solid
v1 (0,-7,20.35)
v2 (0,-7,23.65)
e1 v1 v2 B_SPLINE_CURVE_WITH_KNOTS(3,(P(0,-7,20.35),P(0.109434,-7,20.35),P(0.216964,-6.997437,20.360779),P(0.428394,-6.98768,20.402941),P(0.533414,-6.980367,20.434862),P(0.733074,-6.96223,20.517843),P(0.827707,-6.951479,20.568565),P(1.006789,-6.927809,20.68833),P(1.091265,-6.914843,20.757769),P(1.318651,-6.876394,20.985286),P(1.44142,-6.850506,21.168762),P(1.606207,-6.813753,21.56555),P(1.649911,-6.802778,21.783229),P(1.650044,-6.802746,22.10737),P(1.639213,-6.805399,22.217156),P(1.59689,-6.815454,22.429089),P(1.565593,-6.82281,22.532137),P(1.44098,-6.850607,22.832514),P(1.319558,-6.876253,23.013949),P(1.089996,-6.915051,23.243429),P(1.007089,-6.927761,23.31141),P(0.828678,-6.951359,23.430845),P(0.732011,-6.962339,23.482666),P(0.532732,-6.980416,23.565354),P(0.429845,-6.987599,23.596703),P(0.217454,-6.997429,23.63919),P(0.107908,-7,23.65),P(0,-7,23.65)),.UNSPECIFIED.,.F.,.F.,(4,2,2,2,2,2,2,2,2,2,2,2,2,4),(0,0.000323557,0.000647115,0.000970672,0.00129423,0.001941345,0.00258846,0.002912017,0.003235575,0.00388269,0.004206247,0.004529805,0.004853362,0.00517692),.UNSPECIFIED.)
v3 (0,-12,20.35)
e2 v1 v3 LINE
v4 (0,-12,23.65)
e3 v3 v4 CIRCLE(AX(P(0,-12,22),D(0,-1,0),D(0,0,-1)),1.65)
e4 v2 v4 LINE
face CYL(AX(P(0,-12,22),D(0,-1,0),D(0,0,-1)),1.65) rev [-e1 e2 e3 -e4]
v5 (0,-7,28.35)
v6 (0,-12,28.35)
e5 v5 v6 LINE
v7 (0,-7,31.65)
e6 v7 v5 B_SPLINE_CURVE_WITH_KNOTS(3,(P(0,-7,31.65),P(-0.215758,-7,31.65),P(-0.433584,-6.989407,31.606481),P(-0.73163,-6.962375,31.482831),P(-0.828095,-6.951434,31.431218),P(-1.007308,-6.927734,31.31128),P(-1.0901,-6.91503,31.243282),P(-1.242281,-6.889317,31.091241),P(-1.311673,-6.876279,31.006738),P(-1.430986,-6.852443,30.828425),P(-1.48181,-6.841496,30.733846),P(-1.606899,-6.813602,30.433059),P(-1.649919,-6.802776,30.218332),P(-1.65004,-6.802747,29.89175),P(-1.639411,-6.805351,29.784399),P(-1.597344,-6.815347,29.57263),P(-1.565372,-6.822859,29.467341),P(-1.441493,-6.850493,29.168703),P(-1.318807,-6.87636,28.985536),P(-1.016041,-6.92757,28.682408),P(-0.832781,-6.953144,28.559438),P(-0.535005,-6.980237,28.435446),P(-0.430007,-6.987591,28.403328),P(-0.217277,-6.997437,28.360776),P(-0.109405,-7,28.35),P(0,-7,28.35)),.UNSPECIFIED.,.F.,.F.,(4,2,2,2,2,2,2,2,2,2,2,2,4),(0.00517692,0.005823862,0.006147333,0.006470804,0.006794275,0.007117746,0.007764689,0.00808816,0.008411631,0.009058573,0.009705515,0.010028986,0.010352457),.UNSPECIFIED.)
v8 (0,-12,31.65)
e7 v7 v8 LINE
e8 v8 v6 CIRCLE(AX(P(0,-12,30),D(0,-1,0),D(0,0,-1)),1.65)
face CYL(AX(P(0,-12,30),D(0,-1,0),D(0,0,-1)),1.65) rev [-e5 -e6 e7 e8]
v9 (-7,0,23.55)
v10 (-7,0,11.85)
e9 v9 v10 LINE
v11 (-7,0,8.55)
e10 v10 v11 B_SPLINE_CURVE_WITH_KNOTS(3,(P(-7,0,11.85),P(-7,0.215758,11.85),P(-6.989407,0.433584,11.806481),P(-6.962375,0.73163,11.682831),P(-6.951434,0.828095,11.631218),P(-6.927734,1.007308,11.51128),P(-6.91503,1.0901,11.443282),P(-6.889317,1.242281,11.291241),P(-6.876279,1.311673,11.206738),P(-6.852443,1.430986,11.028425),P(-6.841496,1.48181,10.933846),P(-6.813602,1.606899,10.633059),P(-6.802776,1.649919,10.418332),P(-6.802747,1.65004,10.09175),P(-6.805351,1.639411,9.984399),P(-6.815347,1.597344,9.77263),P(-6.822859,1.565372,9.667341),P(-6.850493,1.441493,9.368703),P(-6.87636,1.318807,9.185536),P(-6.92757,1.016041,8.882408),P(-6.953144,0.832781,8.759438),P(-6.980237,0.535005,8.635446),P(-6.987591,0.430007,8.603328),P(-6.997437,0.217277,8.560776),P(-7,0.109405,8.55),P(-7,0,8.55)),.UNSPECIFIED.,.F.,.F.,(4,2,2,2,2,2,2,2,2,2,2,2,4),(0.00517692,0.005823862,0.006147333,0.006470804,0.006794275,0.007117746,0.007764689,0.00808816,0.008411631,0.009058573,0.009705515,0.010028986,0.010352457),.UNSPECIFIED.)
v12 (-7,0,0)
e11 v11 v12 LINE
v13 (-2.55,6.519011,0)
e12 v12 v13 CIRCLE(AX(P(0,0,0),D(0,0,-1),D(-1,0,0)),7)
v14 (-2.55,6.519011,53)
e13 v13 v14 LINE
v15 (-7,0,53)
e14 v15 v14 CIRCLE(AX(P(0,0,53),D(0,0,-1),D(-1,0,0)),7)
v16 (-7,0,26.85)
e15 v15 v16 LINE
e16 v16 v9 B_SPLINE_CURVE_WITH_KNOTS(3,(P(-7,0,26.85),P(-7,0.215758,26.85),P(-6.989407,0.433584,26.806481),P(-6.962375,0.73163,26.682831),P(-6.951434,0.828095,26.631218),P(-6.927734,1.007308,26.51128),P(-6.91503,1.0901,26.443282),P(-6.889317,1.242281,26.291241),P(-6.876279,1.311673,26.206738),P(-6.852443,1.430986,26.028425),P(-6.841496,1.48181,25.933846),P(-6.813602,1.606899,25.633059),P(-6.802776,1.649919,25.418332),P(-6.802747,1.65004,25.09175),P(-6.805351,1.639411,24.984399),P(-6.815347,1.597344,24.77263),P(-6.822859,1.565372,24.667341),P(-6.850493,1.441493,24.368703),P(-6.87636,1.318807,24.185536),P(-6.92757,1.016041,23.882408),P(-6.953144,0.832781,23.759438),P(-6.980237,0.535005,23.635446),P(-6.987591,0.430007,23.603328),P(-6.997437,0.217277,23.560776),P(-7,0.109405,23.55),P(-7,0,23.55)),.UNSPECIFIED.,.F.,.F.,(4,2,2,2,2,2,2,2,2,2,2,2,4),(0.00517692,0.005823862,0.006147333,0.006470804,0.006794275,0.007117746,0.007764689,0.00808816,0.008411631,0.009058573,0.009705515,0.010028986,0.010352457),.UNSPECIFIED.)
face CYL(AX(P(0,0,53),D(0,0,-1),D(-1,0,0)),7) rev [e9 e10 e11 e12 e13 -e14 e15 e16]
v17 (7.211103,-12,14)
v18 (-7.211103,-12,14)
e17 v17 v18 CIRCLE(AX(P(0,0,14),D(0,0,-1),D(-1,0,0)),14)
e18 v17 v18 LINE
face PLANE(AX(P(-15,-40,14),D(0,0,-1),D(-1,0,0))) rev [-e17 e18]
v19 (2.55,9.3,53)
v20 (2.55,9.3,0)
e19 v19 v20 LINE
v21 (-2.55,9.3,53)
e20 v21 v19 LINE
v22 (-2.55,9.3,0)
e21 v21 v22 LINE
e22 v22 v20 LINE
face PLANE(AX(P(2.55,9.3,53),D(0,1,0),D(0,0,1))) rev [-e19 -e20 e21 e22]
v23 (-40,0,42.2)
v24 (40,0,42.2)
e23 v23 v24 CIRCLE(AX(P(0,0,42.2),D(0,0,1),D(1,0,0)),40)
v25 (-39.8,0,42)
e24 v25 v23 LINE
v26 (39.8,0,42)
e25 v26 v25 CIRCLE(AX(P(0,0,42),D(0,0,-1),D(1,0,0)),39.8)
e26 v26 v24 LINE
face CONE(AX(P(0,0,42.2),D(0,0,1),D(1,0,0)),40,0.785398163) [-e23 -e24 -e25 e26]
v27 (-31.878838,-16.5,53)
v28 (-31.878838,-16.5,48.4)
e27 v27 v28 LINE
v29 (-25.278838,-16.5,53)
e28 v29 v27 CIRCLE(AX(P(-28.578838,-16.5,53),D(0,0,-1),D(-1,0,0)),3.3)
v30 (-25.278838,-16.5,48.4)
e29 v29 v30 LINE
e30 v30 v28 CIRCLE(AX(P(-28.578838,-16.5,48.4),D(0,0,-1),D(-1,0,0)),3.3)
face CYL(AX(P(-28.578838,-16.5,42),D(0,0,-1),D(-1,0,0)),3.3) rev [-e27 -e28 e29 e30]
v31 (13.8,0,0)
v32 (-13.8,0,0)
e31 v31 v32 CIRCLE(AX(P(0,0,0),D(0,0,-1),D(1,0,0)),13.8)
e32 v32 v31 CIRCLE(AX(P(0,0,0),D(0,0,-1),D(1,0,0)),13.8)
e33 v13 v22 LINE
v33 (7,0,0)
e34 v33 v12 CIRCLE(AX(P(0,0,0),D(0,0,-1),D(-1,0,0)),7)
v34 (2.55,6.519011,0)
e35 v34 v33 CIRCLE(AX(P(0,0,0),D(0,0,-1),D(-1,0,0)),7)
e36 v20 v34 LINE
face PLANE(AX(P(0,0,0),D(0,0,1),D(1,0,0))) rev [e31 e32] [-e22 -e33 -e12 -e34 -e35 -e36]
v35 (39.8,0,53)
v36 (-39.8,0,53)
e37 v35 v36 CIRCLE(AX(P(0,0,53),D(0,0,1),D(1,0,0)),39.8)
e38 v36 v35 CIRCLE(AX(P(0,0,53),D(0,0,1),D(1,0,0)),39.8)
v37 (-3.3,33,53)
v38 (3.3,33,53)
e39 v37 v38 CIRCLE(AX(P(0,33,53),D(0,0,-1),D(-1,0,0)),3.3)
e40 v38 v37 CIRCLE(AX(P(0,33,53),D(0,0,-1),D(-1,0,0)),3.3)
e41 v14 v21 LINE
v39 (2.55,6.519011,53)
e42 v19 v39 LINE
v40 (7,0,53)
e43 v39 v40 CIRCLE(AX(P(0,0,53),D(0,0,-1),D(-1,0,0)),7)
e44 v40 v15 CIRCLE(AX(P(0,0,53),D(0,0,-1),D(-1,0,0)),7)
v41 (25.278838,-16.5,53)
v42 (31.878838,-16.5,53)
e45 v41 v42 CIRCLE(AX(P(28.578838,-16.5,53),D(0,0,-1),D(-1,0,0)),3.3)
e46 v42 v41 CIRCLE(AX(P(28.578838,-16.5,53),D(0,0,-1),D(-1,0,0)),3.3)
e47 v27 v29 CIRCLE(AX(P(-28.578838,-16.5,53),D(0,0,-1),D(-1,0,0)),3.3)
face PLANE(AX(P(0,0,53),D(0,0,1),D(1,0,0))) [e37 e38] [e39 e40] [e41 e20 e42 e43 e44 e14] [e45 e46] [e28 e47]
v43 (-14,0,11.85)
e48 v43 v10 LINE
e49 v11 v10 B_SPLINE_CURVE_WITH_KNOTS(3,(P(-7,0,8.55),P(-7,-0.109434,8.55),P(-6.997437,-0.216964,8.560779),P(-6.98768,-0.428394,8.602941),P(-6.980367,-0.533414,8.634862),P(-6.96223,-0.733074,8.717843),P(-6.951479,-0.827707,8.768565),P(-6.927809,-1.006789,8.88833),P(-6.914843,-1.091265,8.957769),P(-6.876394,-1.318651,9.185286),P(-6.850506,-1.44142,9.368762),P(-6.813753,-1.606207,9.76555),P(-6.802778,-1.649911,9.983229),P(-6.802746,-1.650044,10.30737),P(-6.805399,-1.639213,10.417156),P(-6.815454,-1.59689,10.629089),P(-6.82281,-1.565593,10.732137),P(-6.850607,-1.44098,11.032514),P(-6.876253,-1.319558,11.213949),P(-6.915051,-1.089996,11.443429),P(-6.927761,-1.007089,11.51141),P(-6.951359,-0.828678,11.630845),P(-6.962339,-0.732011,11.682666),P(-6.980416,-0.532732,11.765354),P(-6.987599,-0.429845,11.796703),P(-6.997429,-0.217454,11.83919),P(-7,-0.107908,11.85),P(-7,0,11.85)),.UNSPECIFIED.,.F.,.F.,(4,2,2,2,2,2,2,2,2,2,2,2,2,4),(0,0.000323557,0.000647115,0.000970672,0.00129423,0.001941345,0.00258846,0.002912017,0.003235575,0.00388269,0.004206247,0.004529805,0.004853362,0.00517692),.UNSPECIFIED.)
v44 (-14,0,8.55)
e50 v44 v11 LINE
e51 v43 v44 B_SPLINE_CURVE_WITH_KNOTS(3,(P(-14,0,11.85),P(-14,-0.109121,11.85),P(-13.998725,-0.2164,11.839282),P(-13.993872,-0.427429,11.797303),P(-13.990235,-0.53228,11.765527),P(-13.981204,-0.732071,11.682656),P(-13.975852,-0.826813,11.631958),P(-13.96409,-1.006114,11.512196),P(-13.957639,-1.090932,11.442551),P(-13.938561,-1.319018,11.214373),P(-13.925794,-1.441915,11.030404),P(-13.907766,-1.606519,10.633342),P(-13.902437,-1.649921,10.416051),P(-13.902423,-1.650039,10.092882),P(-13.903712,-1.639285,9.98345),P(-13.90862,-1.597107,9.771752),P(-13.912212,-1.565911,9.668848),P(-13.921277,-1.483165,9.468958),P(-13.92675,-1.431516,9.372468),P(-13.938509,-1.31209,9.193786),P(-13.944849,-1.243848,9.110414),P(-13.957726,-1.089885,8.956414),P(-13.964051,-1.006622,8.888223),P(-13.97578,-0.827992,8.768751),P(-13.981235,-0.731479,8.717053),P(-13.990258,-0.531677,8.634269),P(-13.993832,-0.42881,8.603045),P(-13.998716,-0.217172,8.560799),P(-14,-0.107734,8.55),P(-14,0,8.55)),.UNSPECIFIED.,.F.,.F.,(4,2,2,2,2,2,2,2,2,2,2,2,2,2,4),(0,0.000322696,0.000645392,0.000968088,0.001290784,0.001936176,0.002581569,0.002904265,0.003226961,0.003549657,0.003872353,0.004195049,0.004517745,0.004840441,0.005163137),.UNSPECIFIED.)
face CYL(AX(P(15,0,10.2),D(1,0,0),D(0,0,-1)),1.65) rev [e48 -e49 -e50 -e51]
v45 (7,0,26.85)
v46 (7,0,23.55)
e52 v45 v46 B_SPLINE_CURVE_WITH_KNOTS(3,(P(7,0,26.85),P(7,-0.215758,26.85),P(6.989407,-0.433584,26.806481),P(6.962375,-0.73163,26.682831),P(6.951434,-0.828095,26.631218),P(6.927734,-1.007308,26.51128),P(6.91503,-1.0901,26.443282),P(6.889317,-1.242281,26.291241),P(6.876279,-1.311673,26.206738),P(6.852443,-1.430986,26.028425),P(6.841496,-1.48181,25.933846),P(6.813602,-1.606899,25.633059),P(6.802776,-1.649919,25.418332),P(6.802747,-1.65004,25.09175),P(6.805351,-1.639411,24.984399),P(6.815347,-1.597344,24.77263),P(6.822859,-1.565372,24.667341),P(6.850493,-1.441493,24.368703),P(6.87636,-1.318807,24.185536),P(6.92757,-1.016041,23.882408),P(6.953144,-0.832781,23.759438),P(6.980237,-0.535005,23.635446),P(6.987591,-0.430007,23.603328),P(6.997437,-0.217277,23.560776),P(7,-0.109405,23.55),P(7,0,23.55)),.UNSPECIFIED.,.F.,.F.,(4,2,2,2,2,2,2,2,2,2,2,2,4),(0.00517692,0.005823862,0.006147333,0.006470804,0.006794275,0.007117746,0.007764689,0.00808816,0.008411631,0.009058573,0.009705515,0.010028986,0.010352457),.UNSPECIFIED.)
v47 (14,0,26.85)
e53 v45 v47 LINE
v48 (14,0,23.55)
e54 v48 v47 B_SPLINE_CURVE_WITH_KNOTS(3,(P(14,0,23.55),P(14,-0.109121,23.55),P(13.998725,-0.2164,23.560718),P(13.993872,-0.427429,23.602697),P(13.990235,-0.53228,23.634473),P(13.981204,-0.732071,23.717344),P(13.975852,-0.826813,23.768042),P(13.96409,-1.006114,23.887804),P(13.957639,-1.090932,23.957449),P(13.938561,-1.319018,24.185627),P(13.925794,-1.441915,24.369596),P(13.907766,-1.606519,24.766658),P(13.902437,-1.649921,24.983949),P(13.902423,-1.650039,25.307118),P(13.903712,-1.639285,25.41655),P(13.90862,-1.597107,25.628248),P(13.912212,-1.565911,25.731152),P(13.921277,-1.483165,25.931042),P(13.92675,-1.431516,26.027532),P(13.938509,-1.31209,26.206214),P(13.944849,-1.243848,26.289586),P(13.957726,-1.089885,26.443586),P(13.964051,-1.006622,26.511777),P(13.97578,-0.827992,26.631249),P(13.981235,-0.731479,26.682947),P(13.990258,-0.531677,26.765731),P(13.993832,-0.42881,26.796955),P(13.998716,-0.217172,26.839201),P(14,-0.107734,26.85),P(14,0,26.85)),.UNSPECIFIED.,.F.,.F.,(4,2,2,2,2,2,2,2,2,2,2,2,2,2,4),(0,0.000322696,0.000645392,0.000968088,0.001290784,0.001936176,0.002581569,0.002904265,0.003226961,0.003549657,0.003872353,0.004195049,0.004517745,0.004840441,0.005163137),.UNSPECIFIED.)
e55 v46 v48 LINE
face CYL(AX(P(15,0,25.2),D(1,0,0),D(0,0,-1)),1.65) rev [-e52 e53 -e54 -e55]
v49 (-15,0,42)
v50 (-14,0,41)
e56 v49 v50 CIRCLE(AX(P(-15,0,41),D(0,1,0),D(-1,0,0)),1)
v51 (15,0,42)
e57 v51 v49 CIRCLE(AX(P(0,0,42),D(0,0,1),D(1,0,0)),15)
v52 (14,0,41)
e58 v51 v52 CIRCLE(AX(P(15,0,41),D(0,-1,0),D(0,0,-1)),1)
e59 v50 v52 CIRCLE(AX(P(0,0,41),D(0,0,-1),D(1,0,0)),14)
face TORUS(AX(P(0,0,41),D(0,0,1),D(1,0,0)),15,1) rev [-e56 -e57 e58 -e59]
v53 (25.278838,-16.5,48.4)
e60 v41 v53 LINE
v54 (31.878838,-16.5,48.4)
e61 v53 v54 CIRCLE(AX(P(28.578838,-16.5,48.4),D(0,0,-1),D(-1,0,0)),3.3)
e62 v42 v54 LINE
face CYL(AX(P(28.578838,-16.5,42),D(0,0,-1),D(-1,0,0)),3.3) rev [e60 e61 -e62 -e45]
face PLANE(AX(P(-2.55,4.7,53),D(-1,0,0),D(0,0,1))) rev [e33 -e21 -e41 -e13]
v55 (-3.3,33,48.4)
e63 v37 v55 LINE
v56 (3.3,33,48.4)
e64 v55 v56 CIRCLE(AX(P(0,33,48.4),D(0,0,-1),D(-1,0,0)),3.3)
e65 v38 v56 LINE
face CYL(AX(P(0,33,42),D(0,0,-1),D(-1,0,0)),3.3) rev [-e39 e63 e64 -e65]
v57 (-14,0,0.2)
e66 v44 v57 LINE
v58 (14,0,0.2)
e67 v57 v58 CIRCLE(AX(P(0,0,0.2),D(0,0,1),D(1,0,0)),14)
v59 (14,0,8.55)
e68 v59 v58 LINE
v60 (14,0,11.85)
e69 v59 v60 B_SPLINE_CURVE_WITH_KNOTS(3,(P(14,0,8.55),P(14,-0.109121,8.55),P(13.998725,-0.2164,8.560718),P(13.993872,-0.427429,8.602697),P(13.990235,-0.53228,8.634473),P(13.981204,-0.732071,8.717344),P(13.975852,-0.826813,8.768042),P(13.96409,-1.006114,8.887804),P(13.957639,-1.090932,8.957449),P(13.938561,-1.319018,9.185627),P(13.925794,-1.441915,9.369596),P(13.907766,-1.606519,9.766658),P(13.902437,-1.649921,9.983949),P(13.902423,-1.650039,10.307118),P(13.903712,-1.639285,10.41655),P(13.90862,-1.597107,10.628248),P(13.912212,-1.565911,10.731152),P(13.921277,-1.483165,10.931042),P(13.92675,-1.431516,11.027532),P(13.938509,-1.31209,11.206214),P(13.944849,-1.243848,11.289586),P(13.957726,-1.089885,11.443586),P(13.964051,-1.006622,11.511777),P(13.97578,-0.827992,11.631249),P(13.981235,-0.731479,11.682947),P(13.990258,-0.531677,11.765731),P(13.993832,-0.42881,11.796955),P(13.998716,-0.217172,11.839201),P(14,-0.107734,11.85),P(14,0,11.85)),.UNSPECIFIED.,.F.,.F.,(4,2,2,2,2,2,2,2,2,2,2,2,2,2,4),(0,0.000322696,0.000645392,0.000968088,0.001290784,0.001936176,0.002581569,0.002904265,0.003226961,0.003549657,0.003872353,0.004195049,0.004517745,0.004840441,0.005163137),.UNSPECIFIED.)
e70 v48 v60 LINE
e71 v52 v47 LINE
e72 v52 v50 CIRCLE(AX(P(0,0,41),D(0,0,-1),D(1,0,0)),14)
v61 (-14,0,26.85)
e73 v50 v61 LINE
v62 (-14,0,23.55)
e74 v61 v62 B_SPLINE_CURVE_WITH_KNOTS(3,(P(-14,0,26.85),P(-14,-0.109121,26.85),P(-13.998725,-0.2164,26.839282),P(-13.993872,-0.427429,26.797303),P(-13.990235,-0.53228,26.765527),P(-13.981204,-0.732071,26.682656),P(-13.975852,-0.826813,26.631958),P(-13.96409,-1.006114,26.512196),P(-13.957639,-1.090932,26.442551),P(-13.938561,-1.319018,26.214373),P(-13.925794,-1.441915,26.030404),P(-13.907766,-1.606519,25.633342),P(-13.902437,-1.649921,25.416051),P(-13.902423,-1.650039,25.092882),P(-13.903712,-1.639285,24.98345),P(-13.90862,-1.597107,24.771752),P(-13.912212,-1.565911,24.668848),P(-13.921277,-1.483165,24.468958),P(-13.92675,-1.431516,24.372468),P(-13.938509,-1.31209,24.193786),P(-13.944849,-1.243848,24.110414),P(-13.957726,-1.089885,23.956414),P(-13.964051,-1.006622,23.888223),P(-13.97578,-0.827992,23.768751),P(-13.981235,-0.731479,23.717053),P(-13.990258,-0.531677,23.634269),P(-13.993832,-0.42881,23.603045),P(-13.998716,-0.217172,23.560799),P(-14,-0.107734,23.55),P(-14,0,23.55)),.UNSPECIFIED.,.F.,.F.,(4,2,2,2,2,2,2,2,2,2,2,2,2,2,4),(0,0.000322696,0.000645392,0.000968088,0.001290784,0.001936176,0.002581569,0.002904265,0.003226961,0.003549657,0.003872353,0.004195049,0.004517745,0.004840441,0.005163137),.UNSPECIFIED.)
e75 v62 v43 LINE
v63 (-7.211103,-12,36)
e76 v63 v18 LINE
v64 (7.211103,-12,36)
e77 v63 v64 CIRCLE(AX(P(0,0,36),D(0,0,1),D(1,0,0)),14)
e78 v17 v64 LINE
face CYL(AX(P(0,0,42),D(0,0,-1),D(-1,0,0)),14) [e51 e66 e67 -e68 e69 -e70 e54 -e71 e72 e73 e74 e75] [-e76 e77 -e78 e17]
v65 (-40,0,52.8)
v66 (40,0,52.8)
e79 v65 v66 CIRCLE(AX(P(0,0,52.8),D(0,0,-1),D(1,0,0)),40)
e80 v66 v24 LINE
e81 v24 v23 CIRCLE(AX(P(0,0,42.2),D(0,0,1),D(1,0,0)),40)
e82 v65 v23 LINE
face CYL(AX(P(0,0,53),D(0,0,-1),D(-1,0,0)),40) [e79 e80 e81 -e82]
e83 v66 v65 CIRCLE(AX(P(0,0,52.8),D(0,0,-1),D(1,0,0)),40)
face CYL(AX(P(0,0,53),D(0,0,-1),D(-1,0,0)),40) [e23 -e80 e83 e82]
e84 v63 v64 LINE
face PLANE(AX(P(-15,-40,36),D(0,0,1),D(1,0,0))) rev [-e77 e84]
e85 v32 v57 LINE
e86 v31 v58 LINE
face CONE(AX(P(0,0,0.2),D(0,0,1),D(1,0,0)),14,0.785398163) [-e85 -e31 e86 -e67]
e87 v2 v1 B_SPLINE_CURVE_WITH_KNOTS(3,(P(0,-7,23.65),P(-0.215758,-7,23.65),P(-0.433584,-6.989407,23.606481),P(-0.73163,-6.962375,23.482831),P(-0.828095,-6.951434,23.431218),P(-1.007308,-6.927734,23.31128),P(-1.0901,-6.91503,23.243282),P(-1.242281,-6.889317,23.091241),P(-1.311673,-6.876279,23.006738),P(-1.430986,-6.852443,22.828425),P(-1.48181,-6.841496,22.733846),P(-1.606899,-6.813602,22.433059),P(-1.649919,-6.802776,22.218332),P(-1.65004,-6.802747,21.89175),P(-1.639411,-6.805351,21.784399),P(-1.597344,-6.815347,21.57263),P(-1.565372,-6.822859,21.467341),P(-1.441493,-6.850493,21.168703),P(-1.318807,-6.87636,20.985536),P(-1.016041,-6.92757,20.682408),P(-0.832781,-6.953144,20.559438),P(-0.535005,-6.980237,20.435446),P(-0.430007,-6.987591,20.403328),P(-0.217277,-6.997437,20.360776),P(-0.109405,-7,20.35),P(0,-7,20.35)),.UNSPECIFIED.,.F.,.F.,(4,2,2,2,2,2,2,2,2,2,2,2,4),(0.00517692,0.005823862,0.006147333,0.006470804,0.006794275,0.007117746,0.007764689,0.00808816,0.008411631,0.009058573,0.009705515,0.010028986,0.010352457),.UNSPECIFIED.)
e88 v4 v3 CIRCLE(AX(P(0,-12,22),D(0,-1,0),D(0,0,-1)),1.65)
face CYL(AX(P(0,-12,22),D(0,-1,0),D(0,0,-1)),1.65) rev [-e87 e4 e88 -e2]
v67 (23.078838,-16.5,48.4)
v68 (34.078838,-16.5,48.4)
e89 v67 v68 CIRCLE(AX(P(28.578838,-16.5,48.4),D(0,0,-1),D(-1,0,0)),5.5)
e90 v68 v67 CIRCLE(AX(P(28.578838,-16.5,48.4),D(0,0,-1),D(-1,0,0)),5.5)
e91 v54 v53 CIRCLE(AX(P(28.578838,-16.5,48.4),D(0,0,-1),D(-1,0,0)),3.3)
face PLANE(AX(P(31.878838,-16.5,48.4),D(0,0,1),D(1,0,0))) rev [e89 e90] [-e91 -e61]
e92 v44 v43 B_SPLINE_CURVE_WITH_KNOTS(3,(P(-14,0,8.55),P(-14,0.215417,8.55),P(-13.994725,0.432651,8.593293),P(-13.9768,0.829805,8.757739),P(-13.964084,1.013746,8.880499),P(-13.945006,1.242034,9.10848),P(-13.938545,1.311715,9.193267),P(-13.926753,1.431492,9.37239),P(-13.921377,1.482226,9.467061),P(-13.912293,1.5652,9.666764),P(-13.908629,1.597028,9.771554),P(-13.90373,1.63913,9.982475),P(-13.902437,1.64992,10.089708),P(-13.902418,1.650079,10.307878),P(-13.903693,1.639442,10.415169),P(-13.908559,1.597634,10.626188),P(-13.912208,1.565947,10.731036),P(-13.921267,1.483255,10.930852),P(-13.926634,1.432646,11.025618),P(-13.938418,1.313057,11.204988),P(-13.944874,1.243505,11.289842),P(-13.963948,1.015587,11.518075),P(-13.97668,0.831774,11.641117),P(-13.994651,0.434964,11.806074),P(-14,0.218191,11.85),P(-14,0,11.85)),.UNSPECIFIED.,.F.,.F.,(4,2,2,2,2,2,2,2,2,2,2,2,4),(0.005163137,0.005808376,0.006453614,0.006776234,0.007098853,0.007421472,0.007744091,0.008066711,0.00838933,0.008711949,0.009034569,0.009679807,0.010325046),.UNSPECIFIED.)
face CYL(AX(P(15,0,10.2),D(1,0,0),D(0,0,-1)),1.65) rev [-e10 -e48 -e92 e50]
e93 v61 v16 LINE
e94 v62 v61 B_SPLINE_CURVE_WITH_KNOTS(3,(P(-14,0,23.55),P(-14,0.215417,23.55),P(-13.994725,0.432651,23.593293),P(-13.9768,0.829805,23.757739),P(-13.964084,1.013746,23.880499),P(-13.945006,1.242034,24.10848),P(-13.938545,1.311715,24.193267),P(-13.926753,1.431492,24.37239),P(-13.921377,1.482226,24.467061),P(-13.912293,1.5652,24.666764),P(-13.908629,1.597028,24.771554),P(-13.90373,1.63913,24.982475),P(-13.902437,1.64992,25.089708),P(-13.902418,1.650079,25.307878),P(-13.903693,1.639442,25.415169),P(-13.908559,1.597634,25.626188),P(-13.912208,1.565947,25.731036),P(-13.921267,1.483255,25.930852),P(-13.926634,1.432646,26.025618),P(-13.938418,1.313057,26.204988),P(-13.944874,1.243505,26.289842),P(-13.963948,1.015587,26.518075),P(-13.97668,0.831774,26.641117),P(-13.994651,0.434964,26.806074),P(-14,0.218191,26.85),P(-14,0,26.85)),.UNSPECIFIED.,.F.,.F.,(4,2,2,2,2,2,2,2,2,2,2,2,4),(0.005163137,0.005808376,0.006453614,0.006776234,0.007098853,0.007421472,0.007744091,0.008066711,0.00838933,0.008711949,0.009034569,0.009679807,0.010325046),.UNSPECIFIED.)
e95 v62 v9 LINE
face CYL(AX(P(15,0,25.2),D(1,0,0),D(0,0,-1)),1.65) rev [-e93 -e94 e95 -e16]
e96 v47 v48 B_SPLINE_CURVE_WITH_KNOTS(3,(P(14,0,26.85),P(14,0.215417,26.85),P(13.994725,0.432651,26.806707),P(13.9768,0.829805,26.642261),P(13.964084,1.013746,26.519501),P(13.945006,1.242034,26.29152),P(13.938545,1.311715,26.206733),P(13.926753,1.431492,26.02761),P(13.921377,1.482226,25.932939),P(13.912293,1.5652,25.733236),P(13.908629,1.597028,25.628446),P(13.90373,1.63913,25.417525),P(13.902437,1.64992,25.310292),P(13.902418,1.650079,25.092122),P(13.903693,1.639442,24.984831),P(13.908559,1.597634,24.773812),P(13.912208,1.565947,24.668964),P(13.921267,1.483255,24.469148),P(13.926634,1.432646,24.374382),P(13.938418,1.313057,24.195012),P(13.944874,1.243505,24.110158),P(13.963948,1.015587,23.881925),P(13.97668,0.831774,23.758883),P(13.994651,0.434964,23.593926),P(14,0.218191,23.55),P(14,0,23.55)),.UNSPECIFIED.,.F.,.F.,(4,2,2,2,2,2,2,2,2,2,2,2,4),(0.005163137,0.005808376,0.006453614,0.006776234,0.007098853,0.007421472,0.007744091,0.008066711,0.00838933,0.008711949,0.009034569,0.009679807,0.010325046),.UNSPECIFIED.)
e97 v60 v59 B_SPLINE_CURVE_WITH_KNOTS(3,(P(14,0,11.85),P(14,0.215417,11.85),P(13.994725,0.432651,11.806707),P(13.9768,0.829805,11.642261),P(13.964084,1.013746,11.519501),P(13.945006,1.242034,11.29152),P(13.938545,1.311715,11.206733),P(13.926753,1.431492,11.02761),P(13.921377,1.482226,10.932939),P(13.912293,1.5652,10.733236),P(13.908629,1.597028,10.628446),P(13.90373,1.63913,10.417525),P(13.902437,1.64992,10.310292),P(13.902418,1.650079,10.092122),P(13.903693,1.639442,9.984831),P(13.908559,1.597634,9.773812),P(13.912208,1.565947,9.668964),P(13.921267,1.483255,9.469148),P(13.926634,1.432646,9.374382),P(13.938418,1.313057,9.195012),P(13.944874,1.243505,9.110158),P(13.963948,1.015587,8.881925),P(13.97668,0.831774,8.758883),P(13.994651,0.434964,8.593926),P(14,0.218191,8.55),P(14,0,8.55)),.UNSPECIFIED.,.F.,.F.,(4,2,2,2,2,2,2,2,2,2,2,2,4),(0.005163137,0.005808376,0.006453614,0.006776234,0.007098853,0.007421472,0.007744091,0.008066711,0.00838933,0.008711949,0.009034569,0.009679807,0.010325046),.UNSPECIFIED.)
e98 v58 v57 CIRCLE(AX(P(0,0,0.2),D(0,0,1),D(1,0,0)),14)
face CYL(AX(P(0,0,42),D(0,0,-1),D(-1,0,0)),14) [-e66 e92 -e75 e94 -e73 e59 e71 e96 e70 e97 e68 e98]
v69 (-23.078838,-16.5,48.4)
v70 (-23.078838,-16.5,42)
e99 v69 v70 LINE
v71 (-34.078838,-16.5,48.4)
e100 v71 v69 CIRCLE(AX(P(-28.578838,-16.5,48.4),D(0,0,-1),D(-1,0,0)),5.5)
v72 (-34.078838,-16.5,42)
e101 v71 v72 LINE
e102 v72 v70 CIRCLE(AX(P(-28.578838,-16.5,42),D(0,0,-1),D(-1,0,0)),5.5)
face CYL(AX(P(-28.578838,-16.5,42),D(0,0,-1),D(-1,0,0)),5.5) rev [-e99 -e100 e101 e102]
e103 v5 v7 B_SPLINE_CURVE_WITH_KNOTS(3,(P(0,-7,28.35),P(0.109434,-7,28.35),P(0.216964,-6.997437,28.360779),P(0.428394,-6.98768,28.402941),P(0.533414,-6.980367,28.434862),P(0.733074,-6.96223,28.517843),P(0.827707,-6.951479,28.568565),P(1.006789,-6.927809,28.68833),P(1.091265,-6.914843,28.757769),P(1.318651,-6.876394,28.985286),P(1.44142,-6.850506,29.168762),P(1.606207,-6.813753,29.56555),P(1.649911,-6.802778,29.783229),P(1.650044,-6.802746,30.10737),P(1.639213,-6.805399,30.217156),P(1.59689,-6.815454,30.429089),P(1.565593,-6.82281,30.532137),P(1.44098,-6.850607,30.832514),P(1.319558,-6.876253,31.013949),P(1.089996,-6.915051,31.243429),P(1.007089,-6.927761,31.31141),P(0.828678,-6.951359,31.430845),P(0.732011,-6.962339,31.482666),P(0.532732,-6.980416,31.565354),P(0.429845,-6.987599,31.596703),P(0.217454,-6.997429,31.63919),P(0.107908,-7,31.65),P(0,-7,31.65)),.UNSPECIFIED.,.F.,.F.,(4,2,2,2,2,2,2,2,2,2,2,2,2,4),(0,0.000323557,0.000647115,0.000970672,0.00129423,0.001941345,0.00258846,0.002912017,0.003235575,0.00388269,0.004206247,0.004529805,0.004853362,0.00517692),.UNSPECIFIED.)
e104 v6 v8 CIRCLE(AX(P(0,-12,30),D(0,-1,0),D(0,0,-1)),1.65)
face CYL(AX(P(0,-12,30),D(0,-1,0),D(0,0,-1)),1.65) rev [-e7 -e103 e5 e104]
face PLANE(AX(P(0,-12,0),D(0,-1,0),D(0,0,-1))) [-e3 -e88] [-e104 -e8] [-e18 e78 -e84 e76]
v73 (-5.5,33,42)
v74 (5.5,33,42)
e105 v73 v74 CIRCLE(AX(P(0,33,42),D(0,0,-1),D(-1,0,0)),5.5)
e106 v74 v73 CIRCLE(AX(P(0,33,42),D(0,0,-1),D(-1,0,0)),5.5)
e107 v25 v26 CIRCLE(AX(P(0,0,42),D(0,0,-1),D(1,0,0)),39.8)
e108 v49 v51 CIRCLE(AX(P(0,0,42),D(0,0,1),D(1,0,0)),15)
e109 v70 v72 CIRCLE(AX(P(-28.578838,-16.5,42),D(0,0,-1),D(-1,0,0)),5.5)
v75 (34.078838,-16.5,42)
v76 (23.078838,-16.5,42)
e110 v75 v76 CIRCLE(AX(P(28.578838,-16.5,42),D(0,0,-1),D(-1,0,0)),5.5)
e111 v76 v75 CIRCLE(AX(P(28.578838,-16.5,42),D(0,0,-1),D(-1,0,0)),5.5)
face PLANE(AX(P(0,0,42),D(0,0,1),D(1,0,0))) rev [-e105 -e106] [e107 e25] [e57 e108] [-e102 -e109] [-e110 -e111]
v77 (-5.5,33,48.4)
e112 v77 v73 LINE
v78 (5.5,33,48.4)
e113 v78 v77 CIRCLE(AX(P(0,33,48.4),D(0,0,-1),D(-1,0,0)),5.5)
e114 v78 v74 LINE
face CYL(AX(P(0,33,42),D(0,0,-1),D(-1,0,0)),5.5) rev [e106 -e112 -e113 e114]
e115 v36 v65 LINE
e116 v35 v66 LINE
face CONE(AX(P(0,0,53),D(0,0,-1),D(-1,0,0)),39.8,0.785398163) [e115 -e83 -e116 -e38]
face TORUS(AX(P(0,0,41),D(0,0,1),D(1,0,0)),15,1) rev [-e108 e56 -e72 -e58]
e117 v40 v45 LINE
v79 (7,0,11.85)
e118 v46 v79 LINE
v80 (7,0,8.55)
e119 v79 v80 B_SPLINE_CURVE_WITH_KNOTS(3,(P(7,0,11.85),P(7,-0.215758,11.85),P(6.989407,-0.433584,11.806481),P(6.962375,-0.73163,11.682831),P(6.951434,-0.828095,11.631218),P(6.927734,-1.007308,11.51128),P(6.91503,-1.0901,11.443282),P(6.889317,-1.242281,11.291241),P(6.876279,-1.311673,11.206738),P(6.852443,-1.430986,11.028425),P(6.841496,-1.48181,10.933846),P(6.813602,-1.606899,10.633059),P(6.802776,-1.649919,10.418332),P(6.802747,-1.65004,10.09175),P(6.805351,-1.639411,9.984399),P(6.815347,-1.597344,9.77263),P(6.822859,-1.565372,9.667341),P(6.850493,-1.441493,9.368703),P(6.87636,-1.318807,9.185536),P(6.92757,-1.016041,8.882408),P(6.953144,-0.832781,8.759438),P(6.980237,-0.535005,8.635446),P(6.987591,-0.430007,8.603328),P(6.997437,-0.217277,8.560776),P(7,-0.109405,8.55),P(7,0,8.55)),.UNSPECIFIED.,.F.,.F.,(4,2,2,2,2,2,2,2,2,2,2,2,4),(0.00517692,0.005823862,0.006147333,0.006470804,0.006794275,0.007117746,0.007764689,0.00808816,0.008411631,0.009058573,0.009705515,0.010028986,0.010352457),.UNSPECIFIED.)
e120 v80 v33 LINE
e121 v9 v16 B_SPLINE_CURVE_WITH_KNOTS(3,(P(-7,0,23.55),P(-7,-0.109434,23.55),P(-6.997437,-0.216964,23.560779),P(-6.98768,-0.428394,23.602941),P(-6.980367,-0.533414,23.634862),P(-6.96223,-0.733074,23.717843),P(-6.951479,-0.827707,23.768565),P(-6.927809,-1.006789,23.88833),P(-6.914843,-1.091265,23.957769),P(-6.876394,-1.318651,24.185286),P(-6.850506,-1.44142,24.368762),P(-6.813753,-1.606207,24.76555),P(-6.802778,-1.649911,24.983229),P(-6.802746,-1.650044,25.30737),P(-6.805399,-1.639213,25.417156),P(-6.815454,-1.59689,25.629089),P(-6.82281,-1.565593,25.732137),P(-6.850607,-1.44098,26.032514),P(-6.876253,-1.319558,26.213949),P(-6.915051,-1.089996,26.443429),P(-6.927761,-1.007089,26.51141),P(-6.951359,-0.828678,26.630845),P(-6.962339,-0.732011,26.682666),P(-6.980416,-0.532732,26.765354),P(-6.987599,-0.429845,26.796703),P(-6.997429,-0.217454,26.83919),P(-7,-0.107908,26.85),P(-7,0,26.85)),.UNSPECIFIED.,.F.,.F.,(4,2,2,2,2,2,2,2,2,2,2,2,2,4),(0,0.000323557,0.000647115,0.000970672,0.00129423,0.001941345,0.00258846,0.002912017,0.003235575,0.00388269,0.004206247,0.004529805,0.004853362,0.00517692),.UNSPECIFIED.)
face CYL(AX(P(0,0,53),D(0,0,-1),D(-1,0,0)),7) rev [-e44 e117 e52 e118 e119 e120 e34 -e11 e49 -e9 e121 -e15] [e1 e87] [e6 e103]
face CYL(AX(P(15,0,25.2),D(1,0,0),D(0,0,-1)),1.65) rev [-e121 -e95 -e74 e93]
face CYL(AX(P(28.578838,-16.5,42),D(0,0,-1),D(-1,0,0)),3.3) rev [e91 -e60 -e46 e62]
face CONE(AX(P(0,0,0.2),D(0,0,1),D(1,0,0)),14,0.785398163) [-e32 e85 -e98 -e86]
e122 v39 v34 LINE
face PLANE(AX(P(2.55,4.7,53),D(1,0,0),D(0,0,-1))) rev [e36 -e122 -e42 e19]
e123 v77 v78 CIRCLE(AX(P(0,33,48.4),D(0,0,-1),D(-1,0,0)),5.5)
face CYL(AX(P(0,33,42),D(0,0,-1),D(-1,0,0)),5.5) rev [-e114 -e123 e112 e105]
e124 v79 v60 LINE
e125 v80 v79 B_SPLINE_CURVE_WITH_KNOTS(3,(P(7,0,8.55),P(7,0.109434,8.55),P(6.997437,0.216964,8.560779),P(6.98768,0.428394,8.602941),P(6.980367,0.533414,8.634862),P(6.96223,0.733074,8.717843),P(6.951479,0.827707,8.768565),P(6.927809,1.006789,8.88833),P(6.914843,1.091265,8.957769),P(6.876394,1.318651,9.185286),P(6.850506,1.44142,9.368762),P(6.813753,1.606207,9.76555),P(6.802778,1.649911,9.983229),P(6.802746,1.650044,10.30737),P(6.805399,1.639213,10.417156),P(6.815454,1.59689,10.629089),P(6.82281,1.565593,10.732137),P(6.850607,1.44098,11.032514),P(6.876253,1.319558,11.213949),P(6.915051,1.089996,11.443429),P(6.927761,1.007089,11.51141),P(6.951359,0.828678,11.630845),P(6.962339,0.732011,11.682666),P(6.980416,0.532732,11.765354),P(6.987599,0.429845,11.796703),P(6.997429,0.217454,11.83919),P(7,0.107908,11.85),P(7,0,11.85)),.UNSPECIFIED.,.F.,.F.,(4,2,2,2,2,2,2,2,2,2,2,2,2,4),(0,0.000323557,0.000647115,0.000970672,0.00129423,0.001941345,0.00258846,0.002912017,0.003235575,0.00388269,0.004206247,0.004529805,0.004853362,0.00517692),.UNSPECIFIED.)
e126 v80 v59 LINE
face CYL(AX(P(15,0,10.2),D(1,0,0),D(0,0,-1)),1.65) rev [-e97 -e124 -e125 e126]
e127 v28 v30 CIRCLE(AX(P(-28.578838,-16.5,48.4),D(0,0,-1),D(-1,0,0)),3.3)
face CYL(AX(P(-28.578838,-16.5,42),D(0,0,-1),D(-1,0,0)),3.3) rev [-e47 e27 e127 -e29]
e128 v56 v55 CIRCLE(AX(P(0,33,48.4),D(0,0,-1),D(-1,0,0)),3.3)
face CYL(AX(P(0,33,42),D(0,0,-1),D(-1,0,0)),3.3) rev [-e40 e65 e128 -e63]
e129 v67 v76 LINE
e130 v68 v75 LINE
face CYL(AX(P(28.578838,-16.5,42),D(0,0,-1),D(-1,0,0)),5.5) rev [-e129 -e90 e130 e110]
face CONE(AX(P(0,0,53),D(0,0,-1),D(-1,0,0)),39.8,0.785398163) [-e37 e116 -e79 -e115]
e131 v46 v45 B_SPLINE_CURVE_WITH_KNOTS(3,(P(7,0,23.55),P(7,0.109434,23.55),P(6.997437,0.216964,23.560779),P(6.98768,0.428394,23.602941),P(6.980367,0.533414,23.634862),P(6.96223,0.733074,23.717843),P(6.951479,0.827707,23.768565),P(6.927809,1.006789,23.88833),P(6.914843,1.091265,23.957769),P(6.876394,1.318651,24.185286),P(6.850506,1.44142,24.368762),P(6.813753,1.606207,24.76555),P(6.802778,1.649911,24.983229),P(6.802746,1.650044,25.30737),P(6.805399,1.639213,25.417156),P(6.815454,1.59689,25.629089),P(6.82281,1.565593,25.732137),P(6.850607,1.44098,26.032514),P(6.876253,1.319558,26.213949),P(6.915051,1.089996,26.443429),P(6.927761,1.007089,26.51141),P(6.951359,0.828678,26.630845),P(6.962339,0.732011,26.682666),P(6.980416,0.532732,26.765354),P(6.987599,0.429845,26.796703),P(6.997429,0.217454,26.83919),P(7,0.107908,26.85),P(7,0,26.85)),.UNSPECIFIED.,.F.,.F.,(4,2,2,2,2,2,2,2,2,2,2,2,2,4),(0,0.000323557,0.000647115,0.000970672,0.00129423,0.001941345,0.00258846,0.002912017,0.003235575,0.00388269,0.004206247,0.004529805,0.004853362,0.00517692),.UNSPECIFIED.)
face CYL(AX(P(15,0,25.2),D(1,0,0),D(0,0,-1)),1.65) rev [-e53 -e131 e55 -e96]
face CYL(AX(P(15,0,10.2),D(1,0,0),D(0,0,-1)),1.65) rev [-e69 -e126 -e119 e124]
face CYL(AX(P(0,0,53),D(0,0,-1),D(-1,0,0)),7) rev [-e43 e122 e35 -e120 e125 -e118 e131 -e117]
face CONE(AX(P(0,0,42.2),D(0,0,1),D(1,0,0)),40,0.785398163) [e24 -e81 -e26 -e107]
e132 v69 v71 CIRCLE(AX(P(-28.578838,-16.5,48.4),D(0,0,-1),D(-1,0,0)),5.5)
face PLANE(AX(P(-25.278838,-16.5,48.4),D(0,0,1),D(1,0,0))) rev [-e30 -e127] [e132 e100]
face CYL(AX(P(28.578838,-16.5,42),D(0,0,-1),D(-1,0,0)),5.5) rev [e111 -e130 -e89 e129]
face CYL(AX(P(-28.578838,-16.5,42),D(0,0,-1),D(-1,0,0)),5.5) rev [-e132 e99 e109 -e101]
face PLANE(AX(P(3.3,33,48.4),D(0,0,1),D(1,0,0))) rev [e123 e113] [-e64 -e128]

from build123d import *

# Parameters (mm, degrees)
SKETCH_1_R                   = 14
EXTRUDE_1_DEPTH              = 42
SKETCH_2_R                   = 40
EXTRUDE_2_DEPTH              = 11
SKETCH_3_R                   = 7
CUT_EXTRUDE_1_DEPTH          = 78.517739905
HOLE_WIZARD_M6_1_D           = 6.6
HOLE_WIZARD_M6_1_CBORE_D     = 11
HOLE_WIZARD_M6_1_CBORE_DEPTH = 6.4
PATTERN_CIRCULAR_1_COUNT     = 3
SKETCH_9_W                   = 30
SKETCH_9_H                   = 22
CUT_EXTRUDE_3_DEPTH          = 85.338603261
HOLE_WIZARD_M4_2_D           = 3.3
HOLE_WIZARD_M4_2_DEPTH       = 11.5
HOLE_WIZARD_M4_2_TIP         = 0.991420021
SKETCH_12_W                  = 5.1
SKETCH_12_H                  = 4.6
CUT_EXTRUDE_4_DEPTH          = 78.517739974
CHAMFER_1_SIZE               = 0.2
FILLET_1_R                   = 1
HOLE_WIZARD_M4_3_D           = 3.3


with BuildPart() as part:
    # 草图1 → 凸台-拉伸1 (new body)
    with BuildSketch(Plane.XY):
        with Locations(Location((0, 0, 0), (0, 0, 180))):
            Circle(SKETCH_1_R)
    extrude(amount=EXTRUDE_1_DEPTH)

    # 草图2 → 凸台-拉伸2 (add)
    with BuildSketch(Plane.XY.offset(42)):
        Circle(SKETCH_2_R)
    extrude(amount=EXTRUDE_2_DEPTH)

    # 草图3 → 切除-拉伸1 (cut, through all)
    with BuildSketch(Plane(origin=(0, 0, 0), x_dir=(-1, 0, 0), z_dir=(0, 0, -1))):
        Circle(SKETCH_3_R)
    extrude(amount=-CUT_EXTRUDE_1_DEPTH, mode=Mode.SUBTRACT)

    # M6 六角凹头螺钉的柱形沉头孔1 (through all)
    with Locations(Plane(origin=(0, 0, 42), x_dir=(-1, 0, 0), z_dir=(0, 0, -1))):
        with Locations((0, 33)):
            hole_wizard_m6_1 = CounterBoreHole(HOLE_WIZARD_M6_1_D / 2, HOLE_WIZARD_M6_1_CBORE_D / 2, HOLE_WIZARD_M6_1_CBORE_DEPTH)

    # 阵列(圆周)1: M6 六角凹头螺钉的柱形沉头孔1 ×3 about axis
    pattern_circular_1_axis = Axis((0, 0, 0), (0, 0, 1))
    for i in range(1, PATTERN_CIRCULAR_1_COUNT):
        add(hole_wizard_m6_1.rotate(pattern_circular_1_axis, i * 360 / PATTERN_CIRCULAR_1_COUNT), mode=Mode.SUBTRACT)

    # 草图9 → 切除-拉伸3 (cut, through all)
    with BuildSketch(Plane(origin=(0, -12, 0), x_dir=(1, 0, 0), z_dir=(0, 1, 0))):
        with Locations((0, -25)):
            Rectangle(SKETCH_9_W, SKETCH_9_H)
    extrude(amount=-CUT_EXTRUDE_3_DEPTH, mode=Mode.SUBTRACT)

    # M4 螺纹孔2
    with Locations(Plane(origin=(0, -12, 0), x_dir=(-1, 0, 0), z_dir=(0, -1, 0))):
        with Locations((0, -30), (0, -22)):
            Hole(HOLE_WIZARD_M4_2_D / 2, depth=HOLE_WIZARD_M4_2_DEPTH)
            with Locations((0, 0, -(HOLE_WIZARD_M4_2_DEPTH + HOLE_WIZARD_M4_2_TIP / 2))):  # 118° drill point
                Cone(0, HOLE_WIZARD_M4_2_D / 2, HOLE_WIZARD_M4_2_TIP, mode=Mode.SUBTRACT)

    # 草图12 → 切除-拉伸4 (cut, through all)
    with BuildSketch(Plane(origin=(0, 0, 0), x_dir=(-1, 0, 0), z_dir=(0, 0, -1))):
        with Locations((0, 7)):
            Rectangle(SKETCH_12_W, SKETCH_12_H)
    extrude(amount=-CUT_EXTRUDE_4_DEPTH, mode=Mode.SUBTRACT)

    # 倒角1
    chamfer_1_edges = [part.edges().sort_by_distance(p)[0] for p in [
        (14, 0, 0),
        (-40, 0, 42),
        (-40, 0, 53),
    ]]
    chamfer(chamfer_1_edges, length=CHAMFER_1_SIZE)

    # 圆角1
    fillet_1_edges = [part.edges().sort_by_distance(p)[0] for p in [
        (14, 0, 42),
    ]]
    fillet(fillet_1_edges, radius=FILLET_1_R)

    # M4 螺纹孔3 (through all)
    with Locations(Plane(origin=(15, 0, 0), x_dir=(0, 0, -1), z_dir=(1, 0, 0))):
        with Locations((-10.2, 0), (-25.2, 0)):
            Hole(HOLE_WIZARD_M4_3_D / 2)


solid = part.part
